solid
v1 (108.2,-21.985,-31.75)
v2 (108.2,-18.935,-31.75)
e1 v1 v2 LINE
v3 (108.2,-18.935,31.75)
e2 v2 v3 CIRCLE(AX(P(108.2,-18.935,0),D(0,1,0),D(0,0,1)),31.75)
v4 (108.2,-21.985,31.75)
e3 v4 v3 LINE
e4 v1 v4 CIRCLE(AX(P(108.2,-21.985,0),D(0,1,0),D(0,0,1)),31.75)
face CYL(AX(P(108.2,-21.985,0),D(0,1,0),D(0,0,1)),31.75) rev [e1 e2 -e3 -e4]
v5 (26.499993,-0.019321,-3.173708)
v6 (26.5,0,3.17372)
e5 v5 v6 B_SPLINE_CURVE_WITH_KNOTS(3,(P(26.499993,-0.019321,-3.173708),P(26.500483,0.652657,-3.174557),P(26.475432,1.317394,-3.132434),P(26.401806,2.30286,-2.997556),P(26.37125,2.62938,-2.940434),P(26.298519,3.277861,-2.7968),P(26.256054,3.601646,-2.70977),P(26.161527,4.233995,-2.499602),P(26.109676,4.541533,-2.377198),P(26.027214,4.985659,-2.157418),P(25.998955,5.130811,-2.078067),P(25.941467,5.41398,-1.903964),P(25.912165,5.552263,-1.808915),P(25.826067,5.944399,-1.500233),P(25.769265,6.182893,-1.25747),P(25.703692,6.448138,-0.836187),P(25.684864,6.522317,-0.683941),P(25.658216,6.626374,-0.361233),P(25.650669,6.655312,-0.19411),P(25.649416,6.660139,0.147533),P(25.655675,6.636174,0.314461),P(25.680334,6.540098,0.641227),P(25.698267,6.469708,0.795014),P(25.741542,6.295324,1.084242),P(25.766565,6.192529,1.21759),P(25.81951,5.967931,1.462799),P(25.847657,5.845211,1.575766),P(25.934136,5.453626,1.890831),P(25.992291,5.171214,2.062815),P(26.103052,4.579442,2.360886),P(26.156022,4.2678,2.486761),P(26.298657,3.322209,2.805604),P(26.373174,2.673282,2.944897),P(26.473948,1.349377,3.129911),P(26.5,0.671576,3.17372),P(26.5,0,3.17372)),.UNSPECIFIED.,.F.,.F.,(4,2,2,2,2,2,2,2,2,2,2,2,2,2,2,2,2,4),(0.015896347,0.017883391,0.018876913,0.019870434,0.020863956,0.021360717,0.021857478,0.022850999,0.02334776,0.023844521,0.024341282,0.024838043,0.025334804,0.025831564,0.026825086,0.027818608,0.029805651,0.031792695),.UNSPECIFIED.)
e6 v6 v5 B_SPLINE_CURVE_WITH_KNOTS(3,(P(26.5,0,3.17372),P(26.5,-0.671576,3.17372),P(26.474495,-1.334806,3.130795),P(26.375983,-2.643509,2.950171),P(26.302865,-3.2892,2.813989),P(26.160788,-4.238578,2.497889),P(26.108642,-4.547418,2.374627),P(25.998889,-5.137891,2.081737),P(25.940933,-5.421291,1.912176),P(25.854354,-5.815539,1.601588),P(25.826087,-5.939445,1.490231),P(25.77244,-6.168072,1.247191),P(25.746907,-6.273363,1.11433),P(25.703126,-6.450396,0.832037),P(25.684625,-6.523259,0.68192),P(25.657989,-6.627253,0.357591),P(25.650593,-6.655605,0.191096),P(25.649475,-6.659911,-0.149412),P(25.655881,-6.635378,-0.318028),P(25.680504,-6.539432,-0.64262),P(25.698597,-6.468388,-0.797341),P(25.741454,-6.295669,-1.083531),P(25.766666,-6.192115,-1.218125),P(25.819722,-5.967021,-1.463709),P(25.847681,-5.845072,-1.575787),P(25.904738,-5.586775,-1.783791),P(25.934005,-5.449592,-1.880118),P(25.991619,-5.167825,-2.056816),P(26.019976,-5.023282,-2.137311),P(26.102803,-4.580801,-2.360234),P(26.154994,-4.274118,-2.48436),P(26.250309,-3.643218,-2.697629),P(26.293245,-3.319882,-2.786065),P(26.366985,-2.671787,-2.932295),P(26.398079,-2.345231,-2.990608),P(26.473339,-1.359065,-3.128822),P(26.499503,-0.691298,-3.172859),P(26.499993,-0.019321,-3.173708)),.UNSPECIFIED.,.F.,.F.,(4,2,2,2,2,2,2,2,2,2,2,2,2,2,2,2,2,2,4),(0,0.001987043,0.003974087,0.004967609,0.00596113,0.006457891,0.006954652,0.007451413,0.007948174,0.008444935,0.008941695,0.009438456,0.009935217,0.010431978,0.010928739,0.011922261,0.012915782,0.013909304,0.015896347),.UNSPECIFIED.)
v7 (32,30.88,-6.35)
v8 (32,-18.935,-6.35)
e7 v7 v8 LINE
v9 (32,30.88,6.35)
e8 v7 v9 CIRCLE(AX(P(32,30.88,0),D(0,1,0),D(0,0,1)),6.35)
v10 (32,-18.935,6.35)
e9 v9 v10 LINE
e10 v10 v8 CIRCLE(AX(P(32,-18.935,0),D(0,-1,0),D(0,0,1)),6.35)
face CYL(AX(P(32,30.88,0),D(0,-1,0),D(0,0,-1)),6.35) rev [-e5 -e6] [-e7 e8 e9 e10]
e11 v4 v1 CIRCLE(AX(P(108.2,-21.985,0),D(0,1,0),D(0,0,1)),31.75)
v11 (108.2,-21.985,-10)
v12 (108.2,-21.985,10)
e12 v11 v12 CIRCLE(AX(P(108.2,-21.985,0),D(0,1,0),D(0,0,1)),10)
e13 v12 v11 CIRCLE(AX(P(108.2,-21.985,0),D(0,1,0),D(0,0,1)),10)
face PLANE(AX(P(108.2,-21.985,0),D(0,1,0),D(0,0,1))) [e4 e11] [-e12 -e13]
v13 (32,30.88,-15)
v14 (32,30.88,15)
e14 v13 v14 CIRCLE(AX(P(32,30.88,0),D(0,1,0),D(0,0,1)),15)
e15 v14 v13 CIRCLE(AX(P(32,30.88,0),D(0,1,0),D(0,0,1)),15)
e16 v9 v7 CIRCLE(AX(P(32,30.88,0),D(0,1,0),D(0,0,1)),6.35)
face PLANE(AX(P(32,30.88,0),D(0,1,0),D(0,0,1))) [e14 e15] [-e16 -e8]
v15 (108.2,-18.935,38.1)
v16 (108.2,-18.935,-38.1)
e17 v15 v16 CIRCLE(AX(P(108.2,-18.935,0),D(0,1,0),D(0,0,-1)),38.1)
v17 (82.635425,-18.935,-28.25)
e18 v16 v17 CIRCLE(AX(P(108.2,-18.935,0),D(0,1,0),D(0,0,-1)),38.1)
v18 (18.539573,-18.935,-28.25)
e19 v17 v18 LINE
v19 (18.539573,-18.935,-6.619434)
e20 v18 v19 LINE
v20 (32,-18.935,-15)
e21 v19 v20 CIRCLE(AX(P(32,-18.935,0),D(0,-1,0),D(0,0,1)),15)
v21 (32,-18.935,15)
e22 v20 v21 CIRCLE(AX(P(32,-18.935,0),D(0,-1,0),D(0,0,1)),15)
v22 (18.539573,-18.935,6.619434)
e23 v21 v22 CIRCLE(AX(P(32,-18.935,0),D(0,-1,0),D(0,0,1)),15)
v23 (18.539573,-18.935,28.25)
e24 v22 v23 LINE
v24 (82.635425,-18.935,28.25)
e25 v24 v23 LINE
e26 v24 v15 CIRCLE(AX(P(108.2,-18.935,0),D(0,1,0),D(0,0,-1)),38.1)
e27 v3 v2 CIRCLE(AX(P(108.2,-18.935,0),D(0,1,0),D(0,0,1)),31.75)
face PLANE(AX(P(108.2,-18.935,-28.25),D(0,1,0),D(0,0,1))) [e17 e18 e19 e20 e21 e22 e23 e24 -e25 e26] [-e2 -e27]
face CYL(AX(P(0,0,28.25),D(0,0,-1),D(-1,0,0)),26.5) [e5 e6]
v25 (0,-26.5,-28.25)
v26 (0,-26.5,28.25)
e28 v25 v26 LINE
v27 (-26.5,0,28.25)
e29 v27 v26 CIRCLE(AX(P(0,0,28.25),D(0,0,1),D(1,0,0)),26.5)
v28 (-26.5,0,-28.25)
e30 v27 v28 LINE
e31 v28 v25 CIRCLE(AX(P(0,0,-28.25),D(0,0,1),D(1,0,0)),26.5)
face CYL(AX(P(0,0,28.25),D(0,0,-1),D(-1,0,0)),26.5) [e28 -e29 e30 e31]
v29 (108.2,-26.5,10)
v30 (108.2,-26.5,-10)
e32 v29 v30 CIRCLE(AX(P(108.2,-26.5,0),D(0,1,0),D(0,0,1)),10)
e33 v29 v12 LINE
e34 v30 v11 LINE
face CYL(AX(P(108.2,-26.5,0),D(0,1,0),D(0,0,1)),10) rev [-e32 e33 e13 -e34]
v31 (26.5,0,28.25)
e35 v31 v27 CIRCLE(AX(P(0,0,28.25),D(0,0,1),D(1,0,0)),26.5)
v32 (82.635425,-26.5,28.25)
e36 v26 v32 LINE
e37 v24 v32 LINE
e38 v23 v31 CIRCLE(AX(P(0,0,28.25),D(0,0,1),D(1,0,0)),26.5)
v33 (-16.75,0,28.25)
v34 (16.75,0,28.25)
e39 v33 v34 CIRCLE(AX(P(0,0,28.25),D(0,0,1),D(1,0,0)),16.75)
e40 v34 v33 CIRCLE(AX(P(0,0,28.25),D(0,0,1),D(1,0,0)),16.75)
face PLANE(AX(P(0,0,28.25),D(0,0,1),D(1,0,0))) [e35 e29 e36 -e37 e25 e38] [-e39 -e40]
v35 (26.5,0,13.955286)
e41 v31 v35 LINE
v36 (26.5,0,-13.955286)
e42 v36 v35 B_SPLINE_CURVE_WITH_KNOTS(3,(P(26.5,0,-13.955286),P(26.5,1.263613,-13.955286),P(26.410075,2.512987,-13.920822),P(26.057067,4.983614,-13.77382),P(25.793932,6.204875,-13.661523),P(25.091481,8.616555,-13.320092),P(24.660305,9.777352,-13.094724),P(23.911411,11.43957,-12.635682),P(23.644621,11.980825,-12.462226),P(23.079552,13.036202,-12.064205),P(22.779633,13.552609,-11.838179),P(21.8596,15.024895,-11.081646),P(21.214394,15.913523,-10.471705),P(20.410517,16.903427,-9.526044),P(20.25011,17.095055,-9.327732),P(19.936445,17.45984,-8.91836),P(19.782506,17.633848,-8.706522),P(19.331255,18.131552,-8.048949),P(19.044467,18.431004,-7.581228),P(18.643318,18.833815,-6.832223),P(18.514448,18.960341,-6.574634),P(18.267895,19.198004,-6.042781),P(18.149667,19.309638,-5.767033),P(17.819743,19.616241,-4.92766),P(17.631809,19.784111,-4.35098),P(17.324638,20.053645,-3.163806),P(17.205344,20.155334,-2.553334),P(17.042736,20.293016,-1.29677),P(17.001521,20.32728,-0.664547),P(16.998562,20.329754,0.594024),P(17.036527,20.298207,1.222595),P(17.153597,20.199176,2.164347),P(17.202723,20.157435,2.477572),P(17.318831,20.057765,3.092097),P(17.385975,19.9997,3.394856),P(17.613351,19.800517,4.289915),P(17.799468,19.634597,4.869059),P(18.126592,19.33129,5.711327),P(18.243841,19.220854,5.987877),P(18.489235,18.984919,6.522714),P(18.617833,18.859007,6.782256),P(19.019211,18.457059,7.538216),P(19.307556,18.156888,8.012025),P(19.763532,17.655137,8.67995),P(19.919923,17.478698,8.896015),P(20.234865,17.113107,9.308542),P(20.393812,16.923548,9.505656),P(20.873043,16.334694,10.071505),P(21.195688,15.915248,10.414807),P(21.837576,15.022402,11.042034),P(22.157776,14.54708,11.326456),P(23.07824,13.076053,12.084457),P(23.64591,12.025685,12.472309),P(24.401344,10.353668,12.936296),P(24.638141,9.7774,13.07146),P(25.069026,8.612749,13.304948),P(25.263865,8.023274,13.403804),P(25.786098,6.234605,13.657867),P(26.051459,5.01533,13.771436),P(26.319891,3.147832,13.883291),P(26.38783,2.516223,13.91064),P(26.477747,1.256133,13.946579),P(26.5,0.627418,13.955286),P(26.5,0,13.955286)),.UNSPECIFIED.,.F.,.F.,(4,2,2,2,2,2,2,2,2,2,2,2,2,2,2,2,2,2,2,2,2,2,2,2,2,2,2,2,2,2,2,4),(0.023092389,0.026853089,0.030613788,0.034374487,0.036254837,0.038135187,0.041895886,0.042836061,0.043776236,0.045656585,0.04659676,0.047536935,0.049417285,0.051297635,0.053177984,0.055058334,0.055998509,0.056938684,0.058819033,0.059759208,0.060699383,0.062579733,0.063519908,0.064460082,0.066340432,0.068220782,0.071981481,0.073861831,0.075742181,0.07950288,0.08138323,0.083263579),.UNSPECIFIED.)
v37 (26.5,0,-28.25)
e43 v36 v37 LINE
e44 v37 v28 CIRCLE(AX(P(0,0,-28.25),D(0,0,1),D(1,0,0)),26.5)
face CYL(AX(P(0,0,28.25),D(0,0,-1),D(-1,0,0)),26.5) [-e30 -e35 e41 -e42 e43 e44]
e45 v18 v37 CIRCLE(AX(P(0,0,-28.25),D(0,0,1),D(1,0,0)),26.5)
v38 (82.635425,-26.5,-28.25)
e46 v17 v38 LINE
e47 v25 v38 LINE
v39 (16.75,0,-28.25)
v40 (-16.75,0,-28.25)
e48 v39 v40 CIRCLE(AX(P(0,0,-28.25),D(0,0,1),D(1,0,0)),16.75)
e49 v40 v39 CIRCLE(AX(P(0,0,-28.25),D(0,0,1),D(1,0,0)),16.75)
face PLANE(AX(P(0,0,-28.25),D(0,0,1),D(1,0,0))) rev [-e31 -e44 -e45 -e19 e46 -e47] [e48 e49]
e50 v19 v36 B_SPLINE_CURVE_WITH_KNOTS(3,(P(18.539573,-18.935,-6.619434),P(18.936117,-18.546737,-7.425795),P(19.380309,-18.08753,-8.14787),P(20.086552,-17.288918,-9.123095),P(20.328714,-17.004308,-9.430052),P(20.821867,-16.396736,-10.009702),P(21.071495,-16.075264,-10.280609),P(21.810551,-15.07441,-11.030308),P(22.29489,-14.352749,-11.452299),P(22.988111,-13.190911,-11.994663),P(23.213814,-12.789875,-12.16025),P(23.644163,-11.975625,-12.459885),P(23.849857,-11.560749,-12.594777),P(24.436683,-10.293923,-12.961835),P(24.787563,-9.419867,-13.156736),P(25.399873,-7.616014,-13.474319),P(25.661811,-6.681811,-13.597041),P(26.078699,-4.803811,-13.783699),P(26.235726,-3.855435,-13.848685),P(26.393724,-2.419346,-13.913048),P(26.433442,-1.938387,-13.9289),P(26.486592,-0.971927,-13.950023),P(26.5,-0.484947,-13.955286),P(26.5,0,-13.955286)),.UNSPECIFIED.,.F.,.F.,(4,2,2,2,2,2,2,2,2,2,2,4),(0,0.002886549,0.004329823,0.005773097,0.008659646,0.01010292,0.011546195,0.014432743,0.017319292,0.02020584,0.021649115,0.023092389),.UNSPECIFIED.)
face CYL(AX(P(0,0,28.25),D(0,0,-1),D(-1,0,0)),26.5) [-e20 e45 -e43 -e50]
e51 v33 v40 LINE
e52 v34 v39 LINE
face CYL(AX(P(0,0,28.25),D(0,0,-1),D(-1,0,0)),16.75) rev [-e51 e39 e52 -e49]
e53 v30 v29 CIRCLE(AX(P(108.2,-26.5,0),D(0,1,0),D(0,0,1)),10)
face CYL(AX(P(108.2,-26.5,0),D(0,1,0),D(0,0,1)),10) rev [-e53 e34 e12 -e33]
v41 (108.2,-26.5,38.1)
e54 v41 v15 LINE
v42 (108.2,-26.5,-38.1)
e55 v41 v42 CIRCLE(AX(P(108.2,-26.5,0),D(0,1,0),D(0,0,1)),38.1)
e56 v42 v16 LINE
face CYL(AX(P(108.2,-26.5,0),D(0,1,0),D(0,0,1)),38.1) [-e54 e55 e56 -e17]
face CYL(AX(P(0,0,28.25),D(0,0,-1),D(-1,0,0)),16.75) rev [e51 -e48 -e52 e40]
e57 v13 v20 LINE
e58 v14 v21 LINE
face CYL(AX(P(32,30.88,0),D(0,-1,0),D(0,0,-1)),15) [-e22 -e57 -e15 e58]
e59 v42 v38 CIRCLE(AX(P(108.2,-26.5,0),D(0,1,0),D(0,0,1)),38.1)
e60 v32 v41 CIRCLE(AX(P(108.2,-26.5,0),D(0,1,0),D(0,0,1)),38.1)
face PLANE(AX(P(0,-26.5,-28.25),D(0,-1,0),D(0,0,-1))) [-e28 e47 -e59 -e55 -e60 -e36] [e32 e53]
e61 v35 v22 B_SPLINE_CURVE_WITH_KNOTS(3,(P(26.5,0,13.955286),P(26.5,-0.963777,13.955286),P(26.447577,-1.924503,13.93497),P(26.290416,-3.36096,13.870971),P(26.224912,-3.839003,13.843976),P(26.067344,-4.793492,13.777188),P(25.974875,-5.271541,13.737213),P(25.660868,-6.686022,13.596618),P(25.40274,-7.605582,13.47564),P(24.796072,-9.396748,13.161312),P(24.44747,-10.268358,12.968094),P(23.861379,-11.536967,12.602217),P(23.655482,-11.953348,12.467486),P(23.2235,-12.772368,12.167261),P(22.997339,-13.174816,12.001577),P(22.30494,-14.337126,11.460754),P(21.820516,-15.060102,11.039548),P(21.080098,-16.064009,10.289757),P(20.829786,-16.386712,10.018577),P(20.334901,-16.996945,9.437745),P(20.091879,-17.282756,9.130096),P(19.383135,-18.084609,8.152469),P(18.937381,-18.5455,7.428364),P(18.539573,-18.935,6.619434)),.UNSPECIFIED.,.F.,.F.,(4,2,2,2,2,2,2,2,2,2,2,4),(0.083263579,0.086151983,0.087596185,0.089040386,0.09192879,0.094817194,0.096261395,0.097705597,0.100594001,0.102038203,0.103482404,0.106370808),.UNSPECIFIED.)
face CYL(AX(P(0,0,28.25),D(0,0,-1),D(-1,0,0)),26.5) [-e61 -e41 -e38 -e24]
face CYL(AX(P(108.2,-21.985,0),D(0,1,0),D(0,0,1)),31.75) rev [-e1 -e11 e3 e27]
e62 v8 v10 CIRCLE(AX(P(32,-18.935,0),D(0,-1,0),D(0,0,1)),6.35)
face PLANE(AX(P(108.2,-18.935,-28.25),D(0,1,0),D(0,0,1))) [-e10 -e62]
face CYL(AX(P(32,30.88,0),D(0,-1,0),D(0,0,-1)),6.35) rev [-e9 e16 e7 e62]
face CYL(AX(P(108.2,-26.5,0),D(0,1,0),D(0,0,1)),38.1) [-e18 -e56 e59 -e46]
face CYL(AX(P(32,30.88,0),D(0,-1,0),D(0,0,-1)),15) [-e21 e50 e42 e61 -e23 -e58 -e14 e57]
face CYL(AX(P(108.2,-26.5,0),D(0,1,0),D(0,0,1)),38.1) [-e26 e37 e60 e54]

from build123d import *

# Parameters (mm, degrees)
PIVOT_TUBE_SKETCH_R       = 26.5
PIVOT_TUBE_SKETCH_R_2     = 16.75
PIVOT_TUBE_53X_33_5_DEPTH = 28.25
ARM_PLATE_DEPTH           = 28.25
POST_SKETCH_R             = 38.1
POST_SKETCH_R_2           = 31.75
POST_BOSS_DEPTH           = 26.5
POST_TRIM_SKETCH_W        = 76.2
POST_TRIM_SKETCH_H        = 18.935
POST_TRIM_CUT_DEPTH       = 50
MOUNTING_PAD_SKETCH_R     = 31.75
MOUNTING_PAD_DEPTH        = 7.565
PAD_RECESS_SKETCH_R       = 31.75
PAD_RECESS_DEPTH          = 3.05
PAD_HOLE_SKETCH_R         = 10
PAD_HOLE_20_DEPTH         = 159.764275657
ARM_LINK_SKETCH_R         = 15
ARM_LINK_SKETCH_R_2       = 6.35
ARM_LINK_BOSS_DEPTH       = 49.815


with BuildPart() as part:
    # Pivot Tube Sketch → Pivot Tube Ø53xØ33.5 (new, symmetric)
    with BuildSketch(Plane.XY):
        Circle(PIVOT_TUBE_SKETCH_R)
        Circle(PIVOT_TUBE_SKETCH_R_2, mode=Mode.SUBTRACT)
    extrude(amount=PIVOT_TUBE_53X_33_5_DEPTH, both=True)

    # Arm Profile Sketch → Arm Plate (add, symmetric)
    with BuildSketch(Plane.XY):
        with BuildLine():
            Line((0, -26.5), (108.2, -26.5))
            Line((108.2, -26.5), (108.2, -18.935))
            Line((108.2, -18.935), (18.539573215, -18.935))
            ThreePointArc((18.539573215, -18.935), (10.011805531, -24.535968495), (0, -26.5))
        make_face()
    extrude(amount=ARM_PLATE_DEPTH, both=True)

    # Post Sketch → Post Boss (add)
    with BuildSketch(Plane(origin=(0, 0, 0), x_dir=(1, 0, 0), z_dir=(0, 1, 0))):
        with Locations(Location((108.2, 0, 0), (0, 0, 270))):
            Circle(POST_SKETCH_R)
        with Locations(Location((108.2, 0, 0), (0, 0, 270))):
            Circle(POST_SKETCH_R_2, mode=Mode.SUBTRACT)
    extrude(amount=-POST_BOSS_DEPTH)

    # Post Trim Sketch → Post Trim Cut (cut, symmetric)
    with BuildSketch(Plane.XY):
        with Locations((108.2, -9.4675)):
            Rectangle(POST_TRIM_SKETCH_W, POST_TRIM_SKETCH_H)
    extrude(amount=POST_TRIM_CUT_DEPTH, both=True, mode=Mode.SUBTRACT)

    # Mounting Pad Sketch → Mounting Pad (add)
    with BuildSketch(Plane(origin=(0, -18.935, 0), x_dir=(1, 0, 0), z_dir=(0, 1, 0))):
        with Locations((108.2, 0)):
            Circle(MOUNTING_PAD_SKETCH_R)
    extrude(amount=-MOUNTING_PAD_DEPTH)

    # Pad Recess Sketch → Pad Recess (cut)
    with BuildSketch(Plane(origin=(0, -18.935, 0), x_dir=(1, 0, 0), z_dir=(0, 1, 0))):
        with Locations(Location((108.2, 0, 0), (0, 0, 270))):
            Circle(PAD_RECESS_SKETCH_R)
    extrude(amount=-PAD_RECESS_DEPTH, mode=Mode.SUBTRACT)

    # Pad Hole Sketch → Pad Hole Ø20 (cut, through all)
    with BuildSketch(Plane(origin=(0, -21.985, 0), x_dir=(1, 0, 0), z_dir=(0, 1, 0))):
        with Locations(Location((108.2, 0, 0), (0, 0, 270))):
            Circle(PAD_HOLE_SKETCH_R)
    extrude(amount=-PAD_HOLE_20_DEPTH, mode=Mode.SUBTRACT)

    # Arm Link Sketch → Arm Link Boss (add)
    with BuildSketch(Plane(origin=(0, -18.935, 0), x_dir=(1, 0, 0), z_dir=(0, 1, 0))):
        with Locations(Location((32, 0, 0), (0, 0, 153.813423855))):
            Circle(ARM_LINK_SKETCH_R)
        with Locations(Location((32, 0, 0), (0, 0, 270))):
            Circle(ARM_LINK_SKETCH_R_2, mode=Mode.SUBTRACT)
    extrude(amount=ARM_LINK_BOSS_DEPTH)


solid = part.part
